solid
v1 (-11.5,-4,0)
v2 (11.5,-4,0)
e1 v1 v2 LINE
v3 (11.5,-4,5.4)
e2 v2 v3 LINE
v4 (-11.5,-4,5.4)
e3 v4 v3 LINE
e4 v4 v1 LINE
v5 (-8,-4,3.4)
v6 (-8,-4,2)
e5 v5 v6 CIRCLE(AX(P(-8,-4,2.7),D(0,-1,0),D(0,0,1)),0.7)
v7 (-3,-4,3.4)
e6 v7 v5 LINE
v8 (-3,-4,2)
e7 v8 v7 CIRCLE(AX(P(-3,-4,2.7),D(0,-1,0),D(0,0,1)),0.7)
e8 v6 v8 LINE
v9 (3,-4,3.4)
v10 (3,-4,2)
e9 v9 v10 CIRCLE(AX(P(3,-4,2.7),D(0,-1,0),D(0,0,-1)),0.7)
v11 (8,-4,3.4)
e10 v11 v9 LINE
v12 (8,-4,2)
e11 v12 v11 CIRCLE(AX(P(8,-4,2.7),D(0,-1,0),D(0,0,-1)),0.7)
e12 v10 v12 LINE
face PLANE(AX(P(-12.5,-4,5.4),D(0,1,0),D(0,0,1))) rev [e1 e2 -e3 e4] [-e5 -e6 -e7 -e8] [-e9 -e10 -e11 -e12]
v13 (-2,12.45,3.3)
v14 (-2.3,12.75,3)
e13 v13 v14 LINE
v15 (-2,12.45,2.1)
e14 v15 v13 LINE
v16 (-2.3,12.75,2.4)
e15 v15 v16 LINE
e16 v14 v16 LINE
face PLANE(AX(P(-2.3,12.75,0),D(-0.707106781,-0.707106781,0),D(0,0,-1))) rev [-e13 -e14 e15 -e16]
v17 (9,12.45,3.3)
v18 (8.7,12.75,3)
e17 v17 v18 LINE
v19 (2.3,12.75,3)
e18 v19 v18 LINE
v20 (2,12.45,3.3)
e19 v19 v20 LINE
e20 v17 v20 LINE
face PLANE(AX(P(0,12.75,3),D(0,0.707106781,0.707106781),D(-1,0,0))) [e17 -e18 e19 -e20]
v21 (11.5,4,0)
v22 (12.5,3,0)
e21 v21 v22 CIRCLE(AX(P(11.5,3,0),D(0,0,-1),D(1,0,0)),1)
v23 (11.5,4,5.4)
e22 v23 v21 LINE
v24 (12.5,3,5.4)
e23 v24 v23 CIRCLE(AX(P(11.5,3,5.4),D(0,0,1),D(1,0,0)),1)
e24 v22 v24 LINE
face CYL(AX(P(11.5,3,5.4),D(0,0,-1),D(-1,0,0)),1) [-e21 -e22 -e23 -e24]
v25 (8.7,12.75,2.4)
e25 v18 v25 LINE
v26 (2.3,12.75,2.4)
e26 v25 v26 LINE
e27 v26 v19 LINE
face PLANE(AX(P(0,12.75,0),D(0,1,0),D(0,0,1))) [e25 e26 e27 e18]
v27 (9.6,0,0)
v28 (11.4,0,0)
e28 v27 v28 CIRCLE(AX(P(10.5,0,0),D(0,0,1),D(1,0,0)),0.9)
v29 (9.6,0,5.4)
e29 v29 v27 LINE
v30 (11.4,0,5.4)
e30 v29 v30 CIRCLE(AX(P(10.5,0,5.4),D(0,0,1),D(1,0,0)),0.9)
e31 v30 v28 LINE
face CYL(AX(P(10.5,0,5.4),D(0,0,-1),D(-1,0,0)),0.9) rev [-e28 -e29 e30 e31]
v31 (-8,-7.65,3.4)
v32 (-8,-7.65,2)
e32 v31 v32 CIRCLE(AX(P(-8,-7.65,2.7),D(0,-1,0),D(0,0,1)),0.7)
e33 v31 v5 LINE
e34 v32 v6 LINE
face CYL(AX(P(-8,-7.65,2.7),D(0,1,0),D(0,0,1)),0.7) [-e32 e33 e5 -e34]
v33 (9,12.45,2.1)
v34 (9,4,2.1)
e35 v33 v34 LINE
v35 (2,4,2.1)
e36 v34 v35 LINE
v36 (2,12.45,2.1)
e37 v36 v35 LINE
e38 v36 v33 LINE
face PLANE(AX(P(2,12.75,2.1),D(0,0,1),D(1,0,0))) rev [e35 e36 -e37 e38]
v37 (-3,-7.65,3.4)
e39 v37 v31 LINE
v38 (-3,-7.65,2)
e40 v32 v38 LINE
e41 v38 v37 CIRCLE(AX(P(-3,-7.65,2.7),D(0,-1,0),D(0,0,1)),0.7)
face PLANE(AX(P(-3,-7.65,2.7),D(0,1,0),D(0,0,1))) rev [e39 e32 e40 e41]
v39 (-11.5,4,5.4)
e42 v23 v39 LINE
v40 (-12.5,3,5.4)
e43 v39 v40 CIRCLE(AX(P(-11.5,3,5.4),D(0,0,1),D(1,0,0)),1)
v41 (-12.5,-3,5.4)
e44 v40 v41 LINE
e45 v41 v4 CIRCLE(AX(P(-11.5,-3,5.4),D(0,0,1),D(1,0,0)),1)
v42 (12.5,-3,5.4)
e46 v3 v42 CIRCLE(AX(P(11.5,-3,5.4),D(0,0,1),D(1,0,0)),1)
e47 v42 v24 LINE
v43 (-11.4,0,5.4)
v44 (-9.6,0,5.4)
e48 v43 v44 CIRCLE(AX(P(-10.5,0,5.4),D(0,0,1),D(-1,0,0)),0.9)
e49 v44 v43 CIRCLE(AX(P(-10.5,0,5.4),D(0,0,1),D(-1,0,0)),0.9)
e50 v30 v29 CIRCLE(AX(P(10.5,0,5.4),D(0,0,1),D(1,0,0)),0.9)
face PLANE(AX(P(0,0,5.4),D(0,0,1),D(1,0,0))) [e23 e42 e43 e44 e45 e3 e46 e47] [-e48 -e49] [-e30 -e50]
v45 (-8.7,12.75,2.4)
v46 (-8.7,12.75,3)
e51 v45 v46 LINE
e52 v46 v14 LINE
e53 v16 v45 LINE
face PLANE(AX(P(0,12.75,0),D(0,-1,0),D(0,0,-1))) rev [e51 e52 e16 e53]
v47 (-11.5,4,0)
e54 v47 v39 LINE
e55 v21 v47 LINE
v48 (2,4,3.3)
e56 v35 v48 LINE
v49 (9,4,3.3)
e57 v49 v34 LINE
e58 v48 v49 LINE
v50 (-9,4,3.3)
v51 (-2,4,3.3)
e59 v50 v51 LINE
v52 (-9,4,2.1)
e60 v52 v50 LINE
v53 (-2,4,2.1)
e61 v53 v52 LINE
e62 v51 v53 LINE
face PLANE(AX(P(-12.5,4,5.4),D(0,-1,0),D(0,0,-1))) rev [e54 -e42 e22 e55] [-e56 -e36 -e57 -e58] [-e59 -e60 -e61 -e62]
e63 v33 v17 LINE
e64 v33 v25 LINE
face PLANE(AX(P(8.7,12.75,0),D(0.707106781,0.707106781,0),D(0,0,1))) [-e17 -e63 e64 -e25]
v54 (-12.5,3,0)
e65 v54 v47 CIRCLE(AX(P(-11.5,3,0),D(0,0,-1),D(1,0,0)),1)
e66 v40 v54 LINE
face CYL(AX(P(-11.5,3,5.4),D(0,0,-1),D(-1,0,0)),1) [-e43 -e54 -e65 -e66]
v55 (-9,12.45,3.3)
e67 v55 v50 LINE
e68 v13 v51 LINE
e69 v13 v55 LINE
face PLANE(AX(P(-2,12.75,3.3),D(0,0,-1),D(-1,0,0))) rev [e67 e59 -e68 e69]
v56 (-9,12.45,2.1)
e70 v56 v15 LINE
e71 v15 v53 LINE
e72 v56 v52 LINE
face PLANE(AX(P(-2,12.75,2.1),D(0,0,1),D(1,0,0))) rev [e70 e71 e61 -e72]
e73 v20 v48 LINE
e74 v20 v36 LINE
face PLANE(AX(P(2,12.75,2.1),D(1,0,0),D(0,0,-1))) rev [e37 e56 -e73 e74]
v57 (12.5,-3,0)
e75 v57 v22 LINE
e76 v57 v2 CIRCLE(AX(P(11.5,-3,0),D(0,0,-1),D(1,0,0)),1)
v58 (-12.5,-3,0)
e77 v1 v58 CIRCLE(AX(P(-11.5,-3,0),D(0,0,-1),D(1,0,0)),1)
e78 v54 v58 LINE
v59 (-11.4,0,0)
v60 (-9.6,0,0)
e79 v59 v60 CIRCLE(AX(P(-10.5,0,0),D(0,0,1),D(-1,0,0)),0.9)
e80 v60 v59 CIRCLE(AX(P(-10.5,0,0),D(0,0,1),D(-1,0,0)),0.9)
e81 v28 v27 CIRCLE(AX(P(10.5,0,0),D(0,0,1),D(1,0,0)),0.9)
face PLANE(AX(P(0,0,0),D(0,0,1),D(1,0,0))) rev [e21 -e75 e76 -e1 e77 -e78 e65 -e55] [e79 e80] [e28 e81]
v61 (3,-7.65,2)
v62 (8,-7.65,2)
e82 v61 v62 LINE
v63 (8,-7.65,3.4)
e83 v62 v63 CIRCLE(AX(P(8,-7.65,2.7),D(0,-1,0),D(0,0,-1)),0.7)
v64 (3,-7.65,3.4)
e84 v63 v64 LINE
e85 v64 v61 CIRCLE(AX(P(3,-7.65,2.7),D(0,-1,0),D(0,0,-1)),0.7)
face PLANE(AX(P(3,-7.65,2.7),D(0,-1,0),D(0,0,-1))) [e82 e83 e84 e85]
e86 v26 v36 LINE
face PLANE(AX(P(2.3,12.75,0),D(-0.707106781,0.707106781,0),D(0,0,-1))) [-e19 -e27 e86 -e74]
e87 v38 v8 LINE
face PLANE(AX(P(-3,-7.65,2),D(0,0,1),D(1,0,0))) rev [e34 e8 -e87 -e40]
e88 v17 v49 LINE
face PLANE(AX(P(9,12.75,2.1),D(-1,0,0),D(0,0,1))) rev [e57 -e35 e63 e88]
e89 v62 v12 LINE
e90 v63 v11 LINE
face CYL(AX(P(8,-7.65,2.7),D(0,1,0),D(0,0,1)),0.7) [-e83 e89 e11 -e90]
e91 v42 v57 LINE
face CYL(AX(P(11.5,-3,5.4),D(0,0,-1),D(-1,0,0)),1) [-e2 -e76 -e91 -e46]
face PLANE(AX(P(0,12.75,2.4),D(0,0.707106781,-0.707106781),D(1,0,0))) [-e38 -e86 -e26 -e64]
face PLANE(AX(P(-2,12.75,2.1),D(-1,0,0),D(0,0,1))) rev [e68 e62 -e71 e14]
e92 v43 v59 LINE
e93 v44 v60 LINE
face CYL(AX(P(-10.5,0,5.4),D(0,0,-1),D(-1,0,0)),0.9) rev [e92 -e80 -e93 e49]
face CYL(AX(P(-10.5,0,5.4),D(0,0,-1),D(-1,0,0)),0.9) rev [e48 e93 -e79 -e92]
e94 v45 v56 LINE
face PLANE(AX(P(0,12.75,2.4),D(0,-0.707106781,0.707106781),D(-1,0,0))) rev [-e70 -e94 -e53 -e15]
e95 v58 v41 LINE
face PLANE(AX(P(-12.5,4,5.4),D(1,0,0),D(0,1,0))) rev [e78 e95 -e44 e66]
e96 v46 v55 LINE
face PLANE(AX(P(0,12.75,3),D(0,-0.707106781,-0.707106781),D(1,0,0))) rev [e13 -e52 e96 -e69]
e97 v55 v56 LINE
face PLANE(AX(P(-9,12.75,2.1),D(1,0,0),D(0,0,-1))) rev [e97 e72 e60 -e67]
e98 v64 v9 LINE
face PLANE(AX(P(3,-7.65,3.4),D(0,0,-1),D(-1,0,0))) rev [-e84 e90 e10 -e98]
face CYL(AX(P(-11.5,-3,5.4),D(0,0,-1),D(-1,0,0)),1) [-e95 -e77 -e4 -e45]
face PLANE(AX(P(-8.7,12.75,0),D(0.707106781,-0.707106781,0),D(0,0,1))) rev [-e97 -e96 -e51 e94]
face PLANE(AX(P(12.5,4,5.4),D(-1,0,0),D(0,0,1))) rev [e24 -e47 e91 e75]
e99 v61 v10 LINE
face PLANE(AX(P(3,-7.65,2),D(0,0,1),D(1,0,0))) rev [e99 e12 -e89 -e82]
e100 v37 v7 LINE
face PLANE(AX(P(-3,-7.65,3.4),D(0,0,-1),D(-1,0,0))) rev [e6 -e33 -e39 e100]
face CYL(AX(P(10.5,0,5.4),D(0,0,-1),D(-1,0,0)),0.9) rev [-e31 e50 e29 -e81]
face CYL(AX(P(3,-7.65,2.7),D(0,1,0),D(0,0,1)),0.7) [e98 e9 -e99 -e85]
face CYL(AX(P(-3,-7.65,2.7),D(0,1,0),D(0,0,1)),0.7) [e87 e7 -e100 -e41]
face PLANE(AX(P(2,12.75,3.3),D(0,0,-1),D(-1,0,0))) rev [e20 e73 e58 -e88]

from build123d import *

# Parameters (mm, degrees)
SKETCH_1_W      = 25
SKETCH_1_H      = 8
SKETCH_1_R      = 0.9
EXTRUDE_1_DEPTH = 5.4
EXTRUDE_2_DEPTH = 3.65
SKETCH_3_W      = 7
SKETCH_3_H      = 1.2
EXTRUDE_3_DEPTH = 8.75
CHAMFER_1_SIZE  = 0.3
FILLET_1_R      = 1


with BuildPart() as part:
    # 草图1 → 凸台-拉伸1 (new body)
    with BuildSketch(Plane.XY):
        Rectangle(SKETCH_1_W, SKETCH_1_H)
        with Locations(Location((10.5, 0, 0), (0, 0, 180))):
            Circle(SKETCH_1_R, mode=Mode.SUBTRACT)
        with Locations(Location((-10.5, 0, 0), (0, 0, 180))):
            Circle(SKETCH_1_R, mode=Mode.SUBTRACT)
    extrude(amount=EXTRUDE_1_DEPTH)

    # 草图2 → 凸台-拉伸2 (add)
    with BuildSketch(Plane(origin=(0, -4, 0), x_dir=(-1, 0, 0), z_dir=(0, -1, 0))):
        with BuildLine():
            Line((-3, -3.4), (-8, -3.4))
            ThreePointArc((-8, -3.4), (-8.7, -2.7), (-8, -2))
            Line((-8, -2), (-3, -2))
            ThreePointArc((-3, -2), (-2.3, -2.7), (-3, -3.4))
        make_face()
        with BuildLine():
            Line((3, -3.4), (8, -3.4))
            ThreePointArc((8, -3.4), (8.7, -2.7), (8, -2))
            Line((8, -2), (3, -2))
            ThreePointArc((3, -2), (2.3, -2.7), (3, -3.4))
        make_face()
    extrude(amount=EXTRUDE_2_DEPTH)

    # 草图3 → 凸台-拉伸3 (add)
    with BuildSketch(Plane(origin=(0, 4, 0), x_dir=(1, 0, 0), z_dir=(0, 1, 0))):
        with Locations((5.5, -2.7)):
            Rectangle(SKETCH_3_W, SKETCH_3_H)
        with Locations((-5.5, -2.7)):
            Rectangle(SKETCH_3_W, SKETCH_3_H)
    extrude(amount=EXTRUDE_3_DEPTH)

    # 倒角1
    chamfer_1_edges = [part.edges().sort_by_distance(p)[0] for p in [
        (9, 12.75, 2.7),
        (5.5, 12.75, 2.1),
        (2, 12.75, 2.7),
        (5.5, 12.75, 3.3),
        (-2, 12.75, 2.7),
        (-5.5, 12.75, 2.1),
        (-9, 12.75, 2.7),
        (-5.5, 12.75, 3.3),
    ]]
    chamfer(chamfer_1_edges, length=CHAMFER_1_SIZE)

    # 圆角1
    fillet_1_edges = [part.edges().sort_by_distance(p)[0] for p in [
        (12.5, -4, 2.7),
        (-12.5, -4, 2.7),
        (-12.5, 4, 2.7),
        (12.5, 4, 2.7),
    ]]
    fillet(fillet_1_edges, radius=FILLET_1_R)


solid = part.part
